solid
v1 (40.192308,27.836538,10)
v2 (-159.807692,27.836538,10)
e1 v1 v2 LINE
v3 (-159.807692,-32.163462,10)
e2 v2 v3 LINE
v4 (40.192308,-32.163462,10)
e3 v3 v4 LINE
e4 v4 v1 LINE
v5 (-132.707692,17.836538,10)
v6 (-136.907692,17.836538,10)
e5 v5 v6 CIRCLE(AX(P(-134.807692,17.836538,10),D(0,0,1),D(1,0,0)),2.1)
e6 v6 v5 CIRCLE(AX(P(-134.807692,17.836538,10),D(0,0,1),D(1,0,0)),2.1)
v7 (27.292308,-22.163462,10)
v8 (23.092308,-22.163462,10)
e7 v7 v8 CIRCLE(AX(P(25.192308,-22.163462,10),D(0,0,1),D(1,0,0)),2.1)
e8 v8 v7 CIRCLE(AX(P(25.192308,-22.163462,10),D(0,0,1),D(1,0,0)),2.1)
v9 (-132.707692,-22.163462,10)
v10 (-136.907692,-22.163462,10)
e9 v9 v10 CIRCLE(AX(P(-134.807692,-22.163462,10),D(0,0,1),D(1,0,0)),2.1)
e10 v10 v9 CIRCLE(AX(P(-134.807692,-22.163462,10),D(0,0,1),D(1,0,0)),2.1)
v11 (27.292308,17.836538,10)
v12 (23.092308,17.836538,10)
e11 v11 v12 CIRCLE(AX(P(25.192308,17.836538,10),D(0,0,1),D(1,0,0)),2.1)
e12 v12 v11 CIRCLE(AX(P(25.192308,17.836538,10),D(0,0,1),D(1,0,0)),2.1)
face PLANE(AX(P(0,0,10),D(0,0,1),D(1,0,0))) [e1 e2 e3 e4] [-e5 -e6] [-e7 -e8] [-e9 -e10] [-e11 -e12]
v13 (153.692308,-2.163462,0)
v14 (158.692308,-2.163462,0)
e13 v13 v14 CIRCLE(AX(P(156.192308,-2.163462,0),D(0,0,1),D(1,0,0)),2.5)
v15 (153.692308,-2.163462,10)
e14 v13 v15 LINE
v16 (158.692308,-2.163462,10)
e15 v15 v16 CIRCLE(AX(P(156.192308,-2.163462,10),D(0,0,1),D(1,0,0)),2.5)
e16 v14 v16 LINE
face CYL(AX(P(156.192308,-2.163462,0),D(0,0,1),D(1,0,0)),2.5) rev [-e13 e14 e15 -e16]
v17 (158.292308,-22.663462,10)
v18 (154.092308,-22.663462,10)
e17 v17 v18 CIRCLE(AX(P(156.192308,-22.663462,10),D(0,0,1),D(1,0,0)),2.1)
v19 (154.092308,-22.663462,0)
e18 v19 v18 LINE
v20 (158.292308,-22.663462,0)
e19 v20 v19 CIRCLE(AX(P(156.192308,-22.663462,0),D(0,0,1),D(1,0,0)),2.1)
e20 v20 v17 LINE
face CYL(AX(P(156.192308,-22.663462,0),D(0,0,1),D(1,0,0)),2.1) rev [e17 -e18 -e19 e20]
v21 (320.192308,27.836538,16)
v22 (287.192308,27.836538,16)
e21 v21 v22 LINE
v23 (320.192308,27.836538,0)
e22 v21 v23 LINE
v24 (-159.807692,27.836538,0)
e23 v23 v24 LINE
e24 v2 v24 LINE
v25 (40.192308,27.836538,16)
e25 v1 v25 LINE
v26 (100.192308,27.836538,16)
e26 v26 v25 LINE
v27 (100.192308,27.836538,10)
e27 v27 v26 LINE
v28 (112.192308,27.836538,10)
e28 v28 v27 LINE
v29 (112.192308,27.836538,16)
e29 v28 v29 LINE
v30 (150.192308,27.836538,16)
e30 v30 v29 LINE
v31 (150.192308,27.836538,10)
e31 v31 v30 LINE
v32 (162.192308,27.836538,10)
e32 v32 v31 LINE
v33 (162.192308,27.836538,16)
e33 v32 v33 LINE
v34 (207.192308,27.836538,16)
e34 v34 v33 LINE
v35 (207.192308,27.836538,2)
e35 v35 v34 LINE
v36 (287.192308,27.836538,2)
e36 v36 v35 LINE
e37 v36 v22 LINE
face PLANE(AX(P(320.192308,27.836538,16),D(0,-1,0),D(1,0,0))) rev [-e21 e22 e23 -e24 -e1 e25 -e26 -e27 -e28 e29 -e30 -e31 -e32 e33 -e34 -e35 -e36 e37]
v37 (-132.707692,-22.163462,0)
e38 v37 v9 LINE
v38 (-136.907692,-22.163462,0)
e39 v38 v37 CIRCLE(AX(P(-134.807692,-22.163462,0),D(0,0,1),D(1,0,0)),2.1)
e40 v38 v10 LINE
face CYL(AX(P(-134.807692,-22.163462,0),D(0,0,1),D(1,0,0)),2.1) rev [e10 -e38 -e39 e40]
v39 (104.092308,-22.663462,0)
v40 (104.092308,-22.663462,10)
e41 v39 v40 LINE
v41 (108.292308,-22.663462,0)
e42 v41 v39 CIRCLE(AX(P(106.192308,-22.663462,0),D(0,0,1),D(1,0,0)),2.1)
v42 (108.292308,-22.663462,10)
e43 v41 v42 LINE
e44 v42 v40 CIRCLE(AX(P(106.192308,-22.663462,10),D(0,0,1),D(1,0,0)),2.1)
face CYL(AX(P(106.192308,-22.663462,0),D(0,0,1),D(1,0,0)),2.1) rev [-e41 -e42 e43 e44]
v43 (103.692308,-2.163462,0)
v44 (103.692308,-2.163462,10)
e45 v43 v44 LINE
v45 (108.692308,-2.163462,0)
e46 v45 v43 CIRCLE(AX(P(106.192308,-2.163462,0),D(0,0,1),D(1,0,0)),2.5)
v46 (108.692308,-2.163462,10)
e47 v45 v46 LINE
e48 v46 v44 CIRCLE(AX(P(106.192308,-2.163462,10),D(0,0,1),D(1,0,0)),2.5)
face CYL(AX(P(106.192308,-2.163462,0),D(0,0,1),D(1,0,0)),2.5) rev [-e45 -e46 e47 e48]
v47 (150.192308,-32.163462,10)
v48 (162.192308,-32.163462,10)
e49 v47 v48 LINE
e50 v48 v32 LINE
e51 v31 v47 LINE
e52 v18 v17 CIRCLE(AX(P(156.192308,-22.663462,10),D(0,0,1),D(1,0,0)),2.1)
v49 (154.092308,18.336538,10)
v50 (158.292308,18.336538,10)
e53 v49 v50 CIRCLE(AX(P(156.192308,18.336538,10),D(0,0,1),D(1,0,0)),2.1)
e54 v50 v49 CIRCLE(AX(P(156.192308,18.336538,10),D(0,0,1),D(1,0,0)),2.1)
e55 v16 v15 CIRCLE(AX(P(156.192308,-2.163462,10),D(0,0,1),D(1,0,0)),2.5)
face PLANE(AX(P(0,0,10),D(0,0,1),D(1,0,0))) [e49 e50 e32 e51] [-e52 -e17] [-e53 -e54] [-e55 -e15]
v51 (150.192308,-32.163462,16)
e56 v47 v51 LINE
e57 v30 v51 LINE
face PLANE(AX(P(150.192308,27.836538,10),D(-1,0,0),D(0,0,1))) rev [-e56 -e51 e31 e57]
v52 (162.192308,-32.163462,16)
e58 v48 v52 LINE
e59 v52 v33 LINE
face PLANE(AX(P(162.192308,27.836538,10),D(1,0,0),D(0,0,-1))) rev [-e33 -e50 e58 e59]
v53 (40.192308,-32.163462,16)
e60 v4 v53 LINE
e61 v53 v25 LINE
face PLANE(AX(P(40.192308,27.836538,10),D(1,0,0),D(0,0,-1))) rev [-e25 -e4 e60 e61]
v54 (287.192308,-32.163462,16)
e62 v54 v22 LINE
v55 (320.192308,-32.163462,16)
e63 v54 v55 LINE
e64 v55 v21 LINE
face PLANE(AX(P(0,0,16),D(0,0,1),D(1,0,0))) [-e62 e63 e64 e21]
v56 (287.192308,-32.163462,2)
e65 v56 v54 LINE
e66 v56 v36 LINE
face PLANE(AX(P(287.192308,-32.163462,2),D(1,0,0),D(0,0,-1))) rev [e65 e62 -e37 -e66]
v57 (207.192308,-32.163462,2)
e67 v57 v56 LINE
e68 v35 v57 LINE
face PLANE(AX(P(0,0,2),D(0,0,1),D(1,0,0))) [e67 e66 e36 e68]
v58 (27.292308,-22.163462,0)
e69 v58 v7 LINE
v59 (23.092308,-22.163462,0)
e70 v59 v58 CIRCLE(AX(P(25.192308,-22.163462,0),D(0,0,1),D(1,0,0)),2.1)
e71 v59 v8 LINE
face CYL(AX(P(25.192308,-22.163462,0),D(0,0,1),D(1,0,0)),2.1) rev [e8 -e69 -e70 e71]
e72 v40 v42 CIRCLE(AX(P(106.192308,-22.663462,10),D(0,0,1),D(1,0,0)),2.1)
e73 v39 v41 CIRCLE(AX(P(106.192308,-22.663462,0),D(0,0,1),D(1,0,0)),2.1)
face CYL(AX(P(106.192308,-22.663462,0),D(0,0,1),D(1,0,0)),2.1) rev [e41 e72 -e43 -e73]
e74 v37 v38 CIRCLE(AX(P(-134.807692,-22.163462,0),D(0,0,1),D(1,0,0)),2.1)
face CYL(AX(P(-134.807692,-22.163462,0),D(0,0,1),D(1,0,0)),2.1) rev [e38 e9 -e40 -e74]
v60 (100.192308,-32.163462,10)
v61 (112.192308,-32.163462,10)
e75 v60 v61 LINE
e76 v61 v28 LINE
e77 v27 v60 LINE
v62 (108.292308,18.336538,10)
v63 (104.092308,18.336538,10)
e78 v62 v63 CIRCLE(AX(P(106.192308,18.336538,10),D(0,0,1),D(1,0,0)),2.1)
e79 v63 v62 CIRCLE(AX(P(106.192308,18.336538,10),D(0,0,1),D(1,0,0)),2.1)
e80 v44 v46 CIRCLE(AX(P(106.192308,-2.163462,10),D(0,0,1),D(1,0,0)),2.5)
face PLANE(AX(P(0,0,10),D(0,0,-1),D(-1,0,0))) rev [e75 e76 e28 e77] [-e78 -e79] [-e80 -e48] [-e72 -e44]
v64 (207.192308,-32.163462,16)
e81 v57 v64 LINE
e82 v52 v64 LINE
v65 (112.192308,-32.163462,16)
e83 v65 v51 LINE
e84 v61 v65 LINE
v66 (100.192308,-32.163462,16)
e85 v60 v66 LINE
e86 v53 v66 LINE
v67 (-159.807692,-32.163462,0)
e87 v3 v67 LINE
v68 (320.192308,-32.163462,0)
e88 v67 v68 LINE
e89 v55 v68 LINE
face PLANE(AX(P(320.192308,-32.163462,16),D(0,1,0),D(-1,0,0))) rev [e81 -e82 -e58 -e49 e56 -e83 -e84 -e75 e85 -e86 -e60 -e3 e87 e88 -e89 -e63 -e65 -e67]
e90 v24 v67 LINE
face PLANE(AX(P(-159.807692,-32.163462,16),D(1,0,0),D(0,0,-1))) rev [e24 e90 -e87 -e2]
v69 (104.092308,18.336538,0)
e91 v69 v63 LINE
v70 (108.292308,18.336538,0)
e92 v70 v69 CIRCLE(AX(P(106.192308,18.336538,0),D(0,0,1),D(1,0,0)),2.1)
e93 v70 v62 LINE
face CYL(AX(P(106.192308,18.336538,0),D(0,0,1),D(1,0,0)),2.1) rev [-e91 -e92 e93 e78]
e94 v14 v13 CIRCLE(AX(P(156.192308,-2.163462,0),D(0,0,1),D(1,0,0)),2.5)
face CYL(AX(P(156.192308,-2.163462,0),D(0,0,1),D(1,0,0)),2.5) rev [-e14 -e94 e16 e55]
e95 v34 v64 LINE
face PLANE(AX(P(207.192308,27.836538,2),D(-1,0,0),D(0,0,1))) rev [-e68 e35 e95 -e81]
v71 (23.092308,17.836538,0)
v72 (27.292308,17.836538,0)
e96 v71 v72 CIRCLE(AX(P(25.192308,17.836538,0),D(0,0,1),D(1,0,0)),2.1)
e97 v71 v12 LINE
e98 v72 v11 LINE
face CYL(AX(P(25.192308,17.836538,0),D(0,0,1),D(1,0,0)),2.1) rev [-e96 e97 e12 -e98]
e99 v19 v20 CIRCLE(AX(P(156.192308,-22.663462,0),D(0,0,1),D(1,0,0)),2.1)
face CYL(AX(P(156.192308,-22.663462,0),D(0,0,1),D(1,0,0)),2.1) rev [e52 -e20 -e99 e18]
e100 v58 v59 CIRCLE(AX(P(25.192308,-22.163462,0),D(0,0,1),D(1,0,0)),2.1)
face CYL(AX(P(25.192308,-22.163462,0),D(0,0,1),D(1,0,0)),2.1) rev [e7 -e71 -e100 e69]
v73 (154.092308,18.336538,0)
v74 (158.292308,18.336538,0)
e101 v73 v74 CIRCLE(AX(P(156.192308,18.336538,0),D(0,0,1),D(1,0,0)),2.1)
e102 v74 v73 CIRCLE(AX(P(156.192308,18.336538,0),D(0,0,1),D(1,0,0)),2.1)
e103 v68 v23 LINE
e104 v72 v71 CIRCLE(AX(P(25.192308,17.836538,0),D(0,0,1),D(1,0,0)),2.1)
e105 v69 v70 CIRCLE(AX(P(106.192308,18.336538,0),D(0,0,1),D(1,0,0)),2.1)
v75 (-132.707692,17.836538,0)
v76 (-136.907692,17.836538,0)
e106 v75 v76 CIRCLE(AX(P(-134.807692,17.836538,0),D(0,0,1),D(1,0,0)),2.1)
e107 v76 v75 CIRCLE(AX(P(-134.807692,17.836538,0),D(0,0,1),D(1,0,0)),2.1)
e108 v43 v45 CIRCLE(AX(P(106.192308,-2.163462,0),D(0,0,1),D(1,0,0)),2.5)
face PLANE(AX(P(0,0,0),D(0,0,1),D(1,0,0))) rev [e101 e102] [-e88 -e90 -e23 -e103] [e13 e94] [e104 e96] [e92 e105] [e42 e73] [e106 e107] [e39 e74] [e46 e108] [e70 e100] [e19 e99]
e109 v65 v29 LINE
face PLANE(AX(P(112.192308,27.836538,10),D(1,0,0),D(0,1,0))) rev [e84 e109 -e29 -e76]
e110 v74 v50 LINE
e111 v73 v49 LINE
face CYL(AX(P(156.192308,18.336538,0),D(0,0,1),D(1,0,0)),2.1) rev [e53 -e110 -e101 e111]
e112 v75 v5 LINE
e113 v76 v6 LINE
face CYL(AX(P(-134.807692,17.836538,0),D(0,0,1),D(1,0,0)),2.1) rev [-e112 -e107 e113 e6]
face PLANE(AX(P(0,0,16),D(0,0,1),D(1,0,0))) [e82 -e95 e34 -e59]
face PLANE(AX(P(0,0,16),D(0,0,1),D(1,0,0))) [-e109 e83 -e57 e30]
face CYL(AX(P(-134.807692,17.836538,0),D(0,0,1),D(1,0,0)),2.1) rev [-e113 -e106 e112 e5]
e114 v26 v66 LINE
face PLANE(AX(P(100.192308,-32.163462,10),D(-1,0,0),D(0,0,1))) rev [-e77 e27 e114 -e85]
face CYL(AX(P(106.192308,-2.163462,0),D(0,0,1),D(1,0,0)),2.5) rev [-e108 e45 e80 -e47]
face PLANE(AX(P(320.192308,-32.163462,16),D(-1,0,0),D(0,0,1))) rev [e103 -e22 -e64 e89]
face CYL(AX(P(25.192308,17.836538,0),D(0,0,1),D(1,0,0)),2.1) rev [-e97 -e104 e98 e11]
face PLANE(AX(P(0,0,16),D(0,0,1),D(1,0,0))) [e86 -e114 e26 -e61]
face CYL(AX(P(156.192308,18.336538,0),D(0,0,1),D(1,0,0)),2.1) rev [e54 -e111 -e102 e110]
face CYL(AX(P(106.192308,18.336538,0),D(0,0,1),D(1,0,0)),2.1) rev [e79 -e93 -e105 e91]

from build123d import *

# Parameters (mm, degrees)
SKETCH_1_W          = 480
SKETCH_1_H          = 60
EXTRUDE_1_DEPTH     = 16
SKETCH_2_W          = 200
SKETCH_2_H          = 60
CUT_EXTRUDE_1_DEPTH = 6
SKETCH_3_W          = 12
SKETCH_3_H          = 60
CUT_EXTRUDE_2_DEPTH = 6
SKETCH_4_R          = 2.1
SKETCH_4_R_2        = 2.5
CUT_EXTRUDE_3_DEPTH = 322.959006961
SKETCH_5_W          = 80
SKETCH_5_H          = 60
CUT_EXTRUDE_4_DEPTH = 14


with BuildPart() as part:
    # 草图1 → 凸台-拉伸1 (new body)
    with BuildSketch(Plane.XY):
        with Locations((80.192307692, -2.163461538)):
            Rectangle(SKETCH_1_W, SKETCH_1_H)
    extrude(amount=EXTRUDE_1_DEPTH)

    # 草图2 → 切除-拉伸1 (cut)
    with BuildSketch(Plane.XY.offset(16)):
        with Locations((-59.807692308, -2.163461538)):
            Rectangle(SKETCH_2_W, SKETCH_2_H)
    extrude(amount=-CUT_EXTRUDE_1_DEPTH, mode=Mode.SUBTRACT)

    # 草图3 → 切除-拉伸2 (cut)
    with BuildSketch(Plane.XY.offset(16)):
        with Locations((106.192307692, -2.163461538)):
            Rectangle(SKETCH_3_W, SKETCH_3_H)
        with Locations((156.192307692, -2.163461538)):
            Rectangle(SKETCH_3_W, SKETCH_3_H)
    extrude(amount=-CUT_EXTRUDE_2_DEPTH, mode=Mode.SUBTRACT)

    # 草图4 → 切除-拉伸3 (cut, through all)
    with BuildSketch(Plane.XY.offset(10)):
        with Locations((-134.807692308, 17.836538462)):
            Circle(SKETCH_4_R)
        with Locations((-134.807692308, -22.163461538)):
            Circle(SKETCH_4_R)
        with Locations((25.192307692, 17.836538462)):
            Circle(SKETCH_4_R)
        with Locations((25.192307692, -22.163461538)):
            Circle(SKETCH_4_R)
        with Locations((106.192307692, 18.336538462)):
            Circle(SKETCH_4_R)
        with Locations((106.192307692, -22.663461538)):
            Circle(SKETCH_4_R)
        with Locations((156.192307692, 18.336538462)):
            Circle(SKETCH_4_R)
        with Locations((156.192307692, -22.663461538)):
            Circle(SKETCH_4_R)
        with Locations((106.192307692, -2.163461538)):
            Circle(SKETCH_4_R_2)
        with Locations((156.192307692, -2.163461538)):
            Circle(SKETCH_4_R_2)
    extrude(amount=-CUT_EXTRUDE_3_DEPTH, mode=Mode.SUBTRACT)

    # 草图5 → 切除-拉伸4 (cut)
    with BuildSketch(Plane.XY.offset(16)):
        with Locations((247.192307692, -2.163461538)):
            Rectangle(SKETCH_5_W, SKETCH_5_H)
    extrude(amount=-CUT_EXTRUDE_4_DEPTH, mode=Mode.SUBTRACT)


solid = part.part
